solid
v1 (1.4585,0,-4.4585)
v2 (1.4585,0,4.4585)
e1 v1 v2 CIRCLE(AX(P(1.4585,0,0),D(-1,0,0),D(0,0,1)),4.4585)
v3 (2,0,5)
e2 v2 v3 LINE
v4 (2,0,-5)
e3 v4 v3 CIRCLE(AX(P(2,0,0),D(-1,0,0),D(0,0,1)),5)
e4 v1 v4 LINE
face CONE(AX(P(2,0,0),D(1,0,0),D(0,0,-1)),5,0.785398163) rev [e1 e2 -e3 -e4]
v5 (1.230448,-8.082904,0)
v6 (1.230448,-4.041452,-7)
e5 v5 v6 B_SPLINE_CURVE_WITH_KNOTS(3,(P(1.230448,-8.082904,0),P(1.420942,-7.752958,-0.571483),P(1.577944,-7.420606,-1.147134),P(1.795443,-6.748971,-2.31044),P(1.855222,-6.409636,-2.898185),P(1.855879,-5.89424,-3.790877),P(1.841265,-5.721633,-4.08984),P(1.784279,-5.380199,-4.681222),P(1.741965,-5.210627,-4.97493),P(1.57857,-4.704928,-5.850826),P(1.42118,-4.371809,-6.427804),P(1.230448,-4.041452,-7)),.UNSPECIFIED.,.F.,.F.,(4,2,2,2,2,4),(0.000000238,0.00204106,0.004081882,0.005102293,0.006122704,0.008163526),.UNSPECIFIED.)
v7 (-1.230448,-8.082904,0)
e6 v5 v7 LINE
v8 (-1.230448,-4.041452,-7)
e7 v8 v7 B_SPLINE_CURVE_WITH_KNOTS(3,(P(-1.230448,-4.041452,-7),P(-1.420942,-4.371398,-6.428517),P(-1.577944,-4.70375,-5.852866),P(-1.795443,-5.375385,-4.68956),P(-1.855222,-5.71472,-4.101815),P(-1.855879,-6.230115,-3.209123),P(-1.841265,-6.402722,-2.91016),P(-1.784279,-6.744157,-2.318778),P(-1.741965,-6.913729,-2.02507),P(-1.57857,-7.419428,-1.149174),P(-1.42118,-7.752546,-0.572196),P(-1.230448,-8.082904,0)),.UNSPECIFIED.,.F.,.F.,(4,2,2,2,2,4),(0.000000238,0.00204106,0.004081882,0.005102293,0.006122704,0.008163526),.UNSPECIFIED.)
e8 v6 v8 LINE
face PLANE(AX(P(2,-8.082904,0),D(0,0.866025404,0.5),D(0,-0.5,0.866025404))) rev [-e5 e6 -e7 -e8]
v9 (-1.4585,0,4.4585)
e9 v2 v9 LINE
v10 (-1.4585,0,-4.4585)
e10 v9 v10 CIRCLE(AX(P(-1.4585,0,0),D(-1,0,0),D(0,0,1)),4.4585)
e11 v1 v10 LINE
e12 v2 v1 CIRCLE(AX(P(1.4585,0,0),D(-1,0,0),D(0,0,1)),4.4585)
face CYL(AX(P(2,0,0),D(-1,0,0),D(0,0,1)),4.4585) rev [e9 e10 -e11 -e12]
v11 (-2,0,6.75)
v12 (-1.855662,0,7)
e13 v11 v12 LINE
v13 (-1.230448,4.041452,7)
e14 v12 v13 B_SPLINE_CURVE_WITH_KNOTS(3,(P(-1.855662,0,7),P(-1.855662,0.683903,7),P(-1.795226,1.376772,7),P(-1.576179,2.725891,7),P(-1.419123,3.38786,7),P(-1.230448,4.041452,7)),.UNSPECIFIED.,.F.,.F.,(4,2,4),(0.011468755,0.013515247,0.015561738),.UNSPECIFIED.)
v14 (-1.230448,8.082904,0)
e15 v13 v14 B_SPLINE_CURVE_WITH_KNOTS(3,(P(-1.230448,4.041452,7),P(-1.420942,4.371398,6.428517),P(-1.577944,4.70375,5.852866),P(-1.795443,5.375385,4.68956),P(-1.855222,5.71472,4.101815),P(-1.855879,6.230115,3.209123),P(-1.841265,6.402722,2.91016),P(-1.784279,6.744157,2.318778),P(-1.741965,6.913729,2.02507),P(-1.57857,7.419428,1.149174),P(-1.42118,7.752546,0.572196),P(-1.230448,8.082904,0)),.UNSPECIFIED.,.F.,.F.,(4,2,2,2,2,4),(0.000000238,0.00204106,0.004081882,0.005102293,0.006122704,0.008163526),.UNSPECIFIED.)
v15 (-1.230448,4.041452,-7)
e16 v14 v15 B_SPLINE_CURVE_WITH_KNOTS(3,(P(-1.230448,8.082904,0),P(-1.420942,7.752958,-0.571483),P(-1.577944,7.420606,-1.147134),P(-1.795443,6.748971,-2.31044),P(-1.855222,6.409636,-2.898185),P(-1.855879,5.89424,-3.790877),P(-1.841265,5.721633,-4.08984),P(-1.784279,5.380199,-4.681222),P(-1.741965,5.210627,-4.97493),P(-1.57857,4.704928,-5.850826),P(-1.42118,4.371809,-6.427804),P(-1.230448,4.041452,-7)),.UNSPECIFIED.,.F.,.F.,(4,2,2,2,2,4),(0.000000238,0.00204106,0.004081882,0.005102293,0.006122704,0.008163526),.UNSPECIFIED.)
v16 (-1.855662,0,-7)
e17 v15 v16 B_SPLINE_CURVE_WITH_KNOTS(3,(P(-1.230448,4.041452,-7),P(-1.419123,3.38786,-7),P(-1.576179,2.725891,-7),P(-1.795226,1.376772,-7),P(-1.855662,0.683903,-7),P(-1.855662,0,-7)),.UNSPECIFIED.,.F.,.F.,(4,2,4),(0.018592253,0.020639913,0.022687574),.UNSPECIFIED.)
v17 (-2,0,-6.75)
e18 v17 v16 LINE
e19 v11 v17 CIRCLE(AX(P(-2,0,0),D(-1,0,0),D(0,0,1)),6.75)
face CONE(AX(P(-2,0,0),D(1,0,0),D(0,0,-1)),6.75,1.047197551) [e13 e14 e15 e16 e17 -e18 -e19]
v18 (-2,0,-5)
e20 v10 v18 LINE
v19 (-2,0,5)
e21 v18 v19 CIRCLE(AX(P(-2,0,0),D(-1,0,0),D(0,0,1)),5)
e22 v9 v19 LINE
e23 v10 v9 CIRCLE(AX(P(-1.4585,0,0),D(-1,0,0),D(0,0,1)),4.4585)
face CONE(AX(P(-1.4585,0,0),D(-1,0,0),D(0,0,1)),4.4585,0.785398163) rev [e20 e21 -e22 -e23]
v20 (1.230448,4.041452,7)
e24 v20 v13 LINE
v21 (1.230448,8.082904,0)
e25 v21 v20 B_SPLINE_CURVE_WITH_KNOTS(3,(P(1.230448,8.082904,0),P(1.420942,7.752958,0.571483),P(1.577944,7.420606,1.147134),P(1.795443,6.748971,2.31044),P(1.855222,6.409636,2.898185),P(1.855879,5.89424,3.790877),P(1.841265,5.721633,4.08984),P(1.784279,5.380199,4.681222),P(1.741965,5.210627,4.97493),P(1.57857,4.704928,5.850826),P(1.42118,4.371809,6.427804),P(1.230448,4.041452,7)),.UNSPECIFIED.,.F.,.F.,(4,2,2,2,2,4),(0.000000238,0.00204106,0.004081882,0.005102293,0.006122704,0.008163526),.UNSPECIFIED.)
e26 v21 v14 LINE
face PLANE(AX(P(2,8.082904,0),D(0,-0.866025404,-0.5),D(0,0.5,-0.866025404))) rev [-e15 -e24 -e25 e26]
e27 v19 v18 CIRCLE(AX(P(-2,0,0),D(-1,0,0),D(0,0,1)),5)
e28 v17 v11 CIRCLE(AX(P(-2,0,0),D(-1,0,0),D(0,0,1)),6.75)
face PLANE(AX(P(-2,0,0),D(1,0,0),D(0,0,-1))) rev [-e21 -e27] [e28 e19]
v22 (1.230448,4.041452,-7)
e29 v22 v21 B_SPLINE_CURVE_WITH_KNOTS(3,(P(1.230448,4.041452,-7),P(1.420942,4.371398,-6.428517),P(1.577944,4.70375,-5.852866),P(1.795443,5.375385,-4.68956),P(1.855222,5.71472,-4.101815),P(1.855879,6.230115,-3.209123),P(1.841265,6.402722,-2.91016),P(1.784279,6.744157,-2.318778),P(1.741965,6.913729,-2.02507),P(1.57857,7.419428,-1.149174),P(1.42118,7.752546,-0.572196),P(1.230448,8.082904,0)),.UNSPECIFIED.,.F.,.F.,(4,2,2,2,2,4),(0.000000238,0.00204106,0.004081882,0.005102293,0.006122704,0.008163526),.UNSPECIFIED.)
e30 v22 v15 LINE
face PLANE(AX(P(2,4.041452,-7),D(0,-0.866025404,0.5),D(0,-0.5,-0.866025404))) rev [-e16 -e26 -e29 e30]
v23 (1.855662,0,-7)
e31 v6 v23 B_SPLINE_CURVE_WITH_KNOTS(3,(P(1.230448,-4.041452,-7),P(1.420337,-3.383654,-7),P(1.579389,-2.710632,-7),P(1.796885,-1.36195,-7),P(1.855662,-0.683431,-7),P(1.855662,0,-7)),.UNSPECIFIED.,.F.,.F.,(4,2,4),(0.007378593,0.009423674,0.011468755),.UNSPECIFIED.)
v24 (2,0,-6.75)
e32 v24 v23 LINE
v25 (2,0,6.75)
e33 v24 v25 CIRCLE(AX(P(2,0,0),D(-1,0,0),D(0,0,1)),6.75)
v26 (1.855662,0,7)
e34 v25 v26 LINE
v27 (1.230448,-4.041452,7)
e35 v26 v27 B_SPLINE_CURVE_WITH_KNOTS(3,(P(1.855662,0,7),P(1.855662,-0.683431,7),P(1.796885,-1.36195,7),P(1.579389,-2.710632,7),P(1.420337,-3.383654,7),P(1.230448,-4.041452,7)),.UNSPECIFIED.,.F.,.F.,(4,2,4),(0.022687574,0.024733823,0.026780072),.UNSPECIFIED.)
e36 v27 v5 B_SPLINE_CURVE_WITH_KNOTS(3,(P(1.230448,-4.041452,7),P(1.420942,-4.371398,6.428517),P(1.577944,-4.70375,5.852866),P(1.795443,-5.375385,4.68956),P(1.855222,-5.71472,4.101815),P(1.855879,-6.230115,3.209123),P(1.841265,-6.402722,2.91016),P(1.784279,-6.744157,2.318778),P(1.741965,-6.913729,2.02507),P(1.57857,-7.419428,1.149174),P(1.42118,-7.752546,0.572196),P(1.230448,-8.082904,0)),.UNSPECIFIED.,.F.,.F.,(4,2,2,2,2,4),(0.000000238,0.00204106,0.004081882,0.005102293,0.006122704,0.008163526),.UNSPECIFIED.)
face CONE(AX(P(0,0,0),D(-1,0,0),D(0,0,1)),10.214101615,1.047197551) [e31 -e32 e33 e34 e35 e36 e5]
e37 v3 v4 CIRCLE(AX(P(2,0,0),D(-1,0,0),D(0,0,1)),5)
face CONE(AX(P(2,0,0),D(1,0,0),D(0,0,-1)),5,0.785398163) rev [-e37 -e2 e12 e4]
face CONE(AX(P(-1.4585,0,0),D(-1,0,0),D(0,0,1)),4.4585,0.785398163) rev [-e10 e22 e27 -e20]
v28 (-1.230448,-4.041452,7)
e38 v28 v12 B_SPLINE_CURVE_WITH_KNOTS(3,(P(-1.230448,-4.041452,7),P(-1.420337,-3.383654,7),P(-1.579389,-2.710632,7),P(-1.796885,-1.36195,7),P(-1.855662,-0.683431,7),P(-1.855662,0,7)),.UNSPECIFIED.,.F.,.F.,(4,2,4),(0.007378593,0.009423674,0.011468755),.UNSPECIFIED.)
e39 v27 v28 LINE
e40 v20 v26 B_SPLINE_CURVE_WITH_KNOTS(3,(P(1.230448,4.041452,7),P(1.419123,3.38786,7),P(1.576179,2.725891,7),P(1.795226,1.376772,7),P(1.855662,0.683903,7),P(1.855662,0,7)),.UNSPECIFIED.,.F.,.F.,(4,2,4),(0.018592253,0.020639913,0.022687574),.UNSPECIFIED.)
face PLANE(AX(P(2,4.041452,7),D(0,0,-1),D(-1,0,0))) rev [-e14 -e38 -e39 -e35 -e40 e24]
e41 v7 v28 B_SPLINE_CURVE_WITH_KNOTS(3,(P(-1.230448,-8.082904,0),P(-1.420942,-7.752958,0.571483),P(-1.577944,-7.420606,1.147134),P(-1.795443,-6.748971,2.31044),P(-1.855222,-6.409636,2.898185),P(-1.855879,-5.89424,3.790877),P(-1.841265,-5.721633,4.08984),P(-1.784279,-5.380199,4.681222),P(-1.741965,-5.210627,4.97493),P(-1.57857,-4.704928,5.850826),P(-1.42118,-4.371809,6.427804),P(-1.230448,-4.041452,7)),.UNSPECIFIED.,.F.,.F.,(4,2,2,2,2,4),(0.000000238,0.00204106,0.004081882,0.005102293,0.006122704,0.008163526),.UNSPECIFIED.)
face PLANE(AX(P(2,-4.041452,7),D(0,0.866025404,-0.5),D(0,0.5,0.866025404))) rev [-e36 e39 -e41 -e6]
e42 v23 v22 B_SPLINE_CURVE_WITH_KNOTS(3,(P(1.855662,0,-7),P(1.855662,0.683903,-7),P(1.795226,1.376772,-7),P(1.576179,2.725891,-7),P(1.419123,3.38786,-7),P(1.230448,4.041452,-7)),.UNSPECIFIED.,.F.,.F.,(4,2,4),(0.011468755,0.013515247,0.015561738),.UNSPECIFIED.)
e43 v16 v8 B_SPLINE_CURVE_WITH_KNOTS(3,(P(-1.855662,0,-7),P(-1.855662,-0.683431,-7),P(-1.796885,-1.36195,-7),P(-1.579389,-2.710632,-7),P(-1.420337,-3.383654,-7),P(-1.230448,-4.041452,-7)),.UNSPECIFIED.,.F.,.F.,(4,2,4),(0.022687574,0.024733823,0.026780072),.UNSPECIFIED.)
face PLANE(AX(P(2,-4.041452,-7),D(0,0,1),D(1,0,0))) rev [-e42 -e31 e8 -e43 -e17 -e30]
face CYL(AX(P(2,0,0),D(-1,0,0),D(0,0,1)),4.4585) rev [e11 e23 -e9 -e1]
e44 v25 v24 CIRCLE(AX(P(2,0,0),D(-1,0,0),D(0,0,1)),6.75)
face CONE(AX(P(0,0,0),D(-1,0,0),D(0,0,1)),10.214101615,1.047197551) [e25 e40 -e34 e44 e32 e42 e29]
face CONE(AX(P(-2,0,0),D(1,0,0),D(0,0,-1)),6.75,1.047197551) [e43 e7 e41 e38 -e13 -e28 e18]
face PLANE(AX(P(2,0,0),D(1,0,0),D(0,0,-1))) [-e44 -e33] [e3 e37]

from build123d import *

# Parameters (mm, degrees)
BOSS_EXTRUDE1_DEPTH      = 2
BOSS_EXTRUDE1_DEPTH_BACK = 2


with BuildPart() as part:
    # Sketch1 → Boss-Extrude1 (new, two sides: drawn at the far end of the back side and taken through both)
    with BuildSketch(Plane(origin=(0, 0, 0), x_dir=(0, 0, -1), z_dir=(1, 0, 0)).offset(-BOSS_EXTRUDE1_DEPTH_BACK)):
        Polygon((-7, 4.041451884), (-7, -4.041451884), (0, -8.082903769), (7, -4.041451884), (7, 4.041451884), (0, 8.082903769), align=None)
    extrude(amount=BOSS_EXTRUDE1_DEPTH + BOSS_EXTRUDE1_DEPTH_BACK)

    # Sketch2 → Cut-Revolve1 (revolve, cut)
    with BuildSketch(Plane.XY, mode=Mode.PRIVATE) as cut_revolve1_sk:
        Polygon((-2, 0), (-2, 5), (-1.4585, 4.4585), (1.4585, 4.4585), (2, 5), (2, 0), align=None)
    revolve(cut_revolve1_sk.sketch.rotate(Axis((2, 0, 0), (-1, 0, 0)), 270), axis=Axis((2, 0, 0), (-1, 0, 0)), mode=Mode.SUBTRACT)

    # Sketch3 → Cut-Revolve2 (revolve, cut)
    with BuildSketch(Plane.XY, mode=Mode.PRIVATE) as cut_revolve2_sk:
        Polygon((-7, 16.75), (-7, 1), (-2, 1), (-2, 6.75), (0, 10.214101615), (2, 6.75), (2, 1), (7, 1), (7, 16.75), align=None)
    revolve(cut_revolve2_sk.sketch.rotate(Axis((50, 0, 0), (-1, 0, 0)), 270), axis=Axis((50, 0, 0), (-1, 0, 0)), mode=Mode.SUBTRACT)


solid = part.part
